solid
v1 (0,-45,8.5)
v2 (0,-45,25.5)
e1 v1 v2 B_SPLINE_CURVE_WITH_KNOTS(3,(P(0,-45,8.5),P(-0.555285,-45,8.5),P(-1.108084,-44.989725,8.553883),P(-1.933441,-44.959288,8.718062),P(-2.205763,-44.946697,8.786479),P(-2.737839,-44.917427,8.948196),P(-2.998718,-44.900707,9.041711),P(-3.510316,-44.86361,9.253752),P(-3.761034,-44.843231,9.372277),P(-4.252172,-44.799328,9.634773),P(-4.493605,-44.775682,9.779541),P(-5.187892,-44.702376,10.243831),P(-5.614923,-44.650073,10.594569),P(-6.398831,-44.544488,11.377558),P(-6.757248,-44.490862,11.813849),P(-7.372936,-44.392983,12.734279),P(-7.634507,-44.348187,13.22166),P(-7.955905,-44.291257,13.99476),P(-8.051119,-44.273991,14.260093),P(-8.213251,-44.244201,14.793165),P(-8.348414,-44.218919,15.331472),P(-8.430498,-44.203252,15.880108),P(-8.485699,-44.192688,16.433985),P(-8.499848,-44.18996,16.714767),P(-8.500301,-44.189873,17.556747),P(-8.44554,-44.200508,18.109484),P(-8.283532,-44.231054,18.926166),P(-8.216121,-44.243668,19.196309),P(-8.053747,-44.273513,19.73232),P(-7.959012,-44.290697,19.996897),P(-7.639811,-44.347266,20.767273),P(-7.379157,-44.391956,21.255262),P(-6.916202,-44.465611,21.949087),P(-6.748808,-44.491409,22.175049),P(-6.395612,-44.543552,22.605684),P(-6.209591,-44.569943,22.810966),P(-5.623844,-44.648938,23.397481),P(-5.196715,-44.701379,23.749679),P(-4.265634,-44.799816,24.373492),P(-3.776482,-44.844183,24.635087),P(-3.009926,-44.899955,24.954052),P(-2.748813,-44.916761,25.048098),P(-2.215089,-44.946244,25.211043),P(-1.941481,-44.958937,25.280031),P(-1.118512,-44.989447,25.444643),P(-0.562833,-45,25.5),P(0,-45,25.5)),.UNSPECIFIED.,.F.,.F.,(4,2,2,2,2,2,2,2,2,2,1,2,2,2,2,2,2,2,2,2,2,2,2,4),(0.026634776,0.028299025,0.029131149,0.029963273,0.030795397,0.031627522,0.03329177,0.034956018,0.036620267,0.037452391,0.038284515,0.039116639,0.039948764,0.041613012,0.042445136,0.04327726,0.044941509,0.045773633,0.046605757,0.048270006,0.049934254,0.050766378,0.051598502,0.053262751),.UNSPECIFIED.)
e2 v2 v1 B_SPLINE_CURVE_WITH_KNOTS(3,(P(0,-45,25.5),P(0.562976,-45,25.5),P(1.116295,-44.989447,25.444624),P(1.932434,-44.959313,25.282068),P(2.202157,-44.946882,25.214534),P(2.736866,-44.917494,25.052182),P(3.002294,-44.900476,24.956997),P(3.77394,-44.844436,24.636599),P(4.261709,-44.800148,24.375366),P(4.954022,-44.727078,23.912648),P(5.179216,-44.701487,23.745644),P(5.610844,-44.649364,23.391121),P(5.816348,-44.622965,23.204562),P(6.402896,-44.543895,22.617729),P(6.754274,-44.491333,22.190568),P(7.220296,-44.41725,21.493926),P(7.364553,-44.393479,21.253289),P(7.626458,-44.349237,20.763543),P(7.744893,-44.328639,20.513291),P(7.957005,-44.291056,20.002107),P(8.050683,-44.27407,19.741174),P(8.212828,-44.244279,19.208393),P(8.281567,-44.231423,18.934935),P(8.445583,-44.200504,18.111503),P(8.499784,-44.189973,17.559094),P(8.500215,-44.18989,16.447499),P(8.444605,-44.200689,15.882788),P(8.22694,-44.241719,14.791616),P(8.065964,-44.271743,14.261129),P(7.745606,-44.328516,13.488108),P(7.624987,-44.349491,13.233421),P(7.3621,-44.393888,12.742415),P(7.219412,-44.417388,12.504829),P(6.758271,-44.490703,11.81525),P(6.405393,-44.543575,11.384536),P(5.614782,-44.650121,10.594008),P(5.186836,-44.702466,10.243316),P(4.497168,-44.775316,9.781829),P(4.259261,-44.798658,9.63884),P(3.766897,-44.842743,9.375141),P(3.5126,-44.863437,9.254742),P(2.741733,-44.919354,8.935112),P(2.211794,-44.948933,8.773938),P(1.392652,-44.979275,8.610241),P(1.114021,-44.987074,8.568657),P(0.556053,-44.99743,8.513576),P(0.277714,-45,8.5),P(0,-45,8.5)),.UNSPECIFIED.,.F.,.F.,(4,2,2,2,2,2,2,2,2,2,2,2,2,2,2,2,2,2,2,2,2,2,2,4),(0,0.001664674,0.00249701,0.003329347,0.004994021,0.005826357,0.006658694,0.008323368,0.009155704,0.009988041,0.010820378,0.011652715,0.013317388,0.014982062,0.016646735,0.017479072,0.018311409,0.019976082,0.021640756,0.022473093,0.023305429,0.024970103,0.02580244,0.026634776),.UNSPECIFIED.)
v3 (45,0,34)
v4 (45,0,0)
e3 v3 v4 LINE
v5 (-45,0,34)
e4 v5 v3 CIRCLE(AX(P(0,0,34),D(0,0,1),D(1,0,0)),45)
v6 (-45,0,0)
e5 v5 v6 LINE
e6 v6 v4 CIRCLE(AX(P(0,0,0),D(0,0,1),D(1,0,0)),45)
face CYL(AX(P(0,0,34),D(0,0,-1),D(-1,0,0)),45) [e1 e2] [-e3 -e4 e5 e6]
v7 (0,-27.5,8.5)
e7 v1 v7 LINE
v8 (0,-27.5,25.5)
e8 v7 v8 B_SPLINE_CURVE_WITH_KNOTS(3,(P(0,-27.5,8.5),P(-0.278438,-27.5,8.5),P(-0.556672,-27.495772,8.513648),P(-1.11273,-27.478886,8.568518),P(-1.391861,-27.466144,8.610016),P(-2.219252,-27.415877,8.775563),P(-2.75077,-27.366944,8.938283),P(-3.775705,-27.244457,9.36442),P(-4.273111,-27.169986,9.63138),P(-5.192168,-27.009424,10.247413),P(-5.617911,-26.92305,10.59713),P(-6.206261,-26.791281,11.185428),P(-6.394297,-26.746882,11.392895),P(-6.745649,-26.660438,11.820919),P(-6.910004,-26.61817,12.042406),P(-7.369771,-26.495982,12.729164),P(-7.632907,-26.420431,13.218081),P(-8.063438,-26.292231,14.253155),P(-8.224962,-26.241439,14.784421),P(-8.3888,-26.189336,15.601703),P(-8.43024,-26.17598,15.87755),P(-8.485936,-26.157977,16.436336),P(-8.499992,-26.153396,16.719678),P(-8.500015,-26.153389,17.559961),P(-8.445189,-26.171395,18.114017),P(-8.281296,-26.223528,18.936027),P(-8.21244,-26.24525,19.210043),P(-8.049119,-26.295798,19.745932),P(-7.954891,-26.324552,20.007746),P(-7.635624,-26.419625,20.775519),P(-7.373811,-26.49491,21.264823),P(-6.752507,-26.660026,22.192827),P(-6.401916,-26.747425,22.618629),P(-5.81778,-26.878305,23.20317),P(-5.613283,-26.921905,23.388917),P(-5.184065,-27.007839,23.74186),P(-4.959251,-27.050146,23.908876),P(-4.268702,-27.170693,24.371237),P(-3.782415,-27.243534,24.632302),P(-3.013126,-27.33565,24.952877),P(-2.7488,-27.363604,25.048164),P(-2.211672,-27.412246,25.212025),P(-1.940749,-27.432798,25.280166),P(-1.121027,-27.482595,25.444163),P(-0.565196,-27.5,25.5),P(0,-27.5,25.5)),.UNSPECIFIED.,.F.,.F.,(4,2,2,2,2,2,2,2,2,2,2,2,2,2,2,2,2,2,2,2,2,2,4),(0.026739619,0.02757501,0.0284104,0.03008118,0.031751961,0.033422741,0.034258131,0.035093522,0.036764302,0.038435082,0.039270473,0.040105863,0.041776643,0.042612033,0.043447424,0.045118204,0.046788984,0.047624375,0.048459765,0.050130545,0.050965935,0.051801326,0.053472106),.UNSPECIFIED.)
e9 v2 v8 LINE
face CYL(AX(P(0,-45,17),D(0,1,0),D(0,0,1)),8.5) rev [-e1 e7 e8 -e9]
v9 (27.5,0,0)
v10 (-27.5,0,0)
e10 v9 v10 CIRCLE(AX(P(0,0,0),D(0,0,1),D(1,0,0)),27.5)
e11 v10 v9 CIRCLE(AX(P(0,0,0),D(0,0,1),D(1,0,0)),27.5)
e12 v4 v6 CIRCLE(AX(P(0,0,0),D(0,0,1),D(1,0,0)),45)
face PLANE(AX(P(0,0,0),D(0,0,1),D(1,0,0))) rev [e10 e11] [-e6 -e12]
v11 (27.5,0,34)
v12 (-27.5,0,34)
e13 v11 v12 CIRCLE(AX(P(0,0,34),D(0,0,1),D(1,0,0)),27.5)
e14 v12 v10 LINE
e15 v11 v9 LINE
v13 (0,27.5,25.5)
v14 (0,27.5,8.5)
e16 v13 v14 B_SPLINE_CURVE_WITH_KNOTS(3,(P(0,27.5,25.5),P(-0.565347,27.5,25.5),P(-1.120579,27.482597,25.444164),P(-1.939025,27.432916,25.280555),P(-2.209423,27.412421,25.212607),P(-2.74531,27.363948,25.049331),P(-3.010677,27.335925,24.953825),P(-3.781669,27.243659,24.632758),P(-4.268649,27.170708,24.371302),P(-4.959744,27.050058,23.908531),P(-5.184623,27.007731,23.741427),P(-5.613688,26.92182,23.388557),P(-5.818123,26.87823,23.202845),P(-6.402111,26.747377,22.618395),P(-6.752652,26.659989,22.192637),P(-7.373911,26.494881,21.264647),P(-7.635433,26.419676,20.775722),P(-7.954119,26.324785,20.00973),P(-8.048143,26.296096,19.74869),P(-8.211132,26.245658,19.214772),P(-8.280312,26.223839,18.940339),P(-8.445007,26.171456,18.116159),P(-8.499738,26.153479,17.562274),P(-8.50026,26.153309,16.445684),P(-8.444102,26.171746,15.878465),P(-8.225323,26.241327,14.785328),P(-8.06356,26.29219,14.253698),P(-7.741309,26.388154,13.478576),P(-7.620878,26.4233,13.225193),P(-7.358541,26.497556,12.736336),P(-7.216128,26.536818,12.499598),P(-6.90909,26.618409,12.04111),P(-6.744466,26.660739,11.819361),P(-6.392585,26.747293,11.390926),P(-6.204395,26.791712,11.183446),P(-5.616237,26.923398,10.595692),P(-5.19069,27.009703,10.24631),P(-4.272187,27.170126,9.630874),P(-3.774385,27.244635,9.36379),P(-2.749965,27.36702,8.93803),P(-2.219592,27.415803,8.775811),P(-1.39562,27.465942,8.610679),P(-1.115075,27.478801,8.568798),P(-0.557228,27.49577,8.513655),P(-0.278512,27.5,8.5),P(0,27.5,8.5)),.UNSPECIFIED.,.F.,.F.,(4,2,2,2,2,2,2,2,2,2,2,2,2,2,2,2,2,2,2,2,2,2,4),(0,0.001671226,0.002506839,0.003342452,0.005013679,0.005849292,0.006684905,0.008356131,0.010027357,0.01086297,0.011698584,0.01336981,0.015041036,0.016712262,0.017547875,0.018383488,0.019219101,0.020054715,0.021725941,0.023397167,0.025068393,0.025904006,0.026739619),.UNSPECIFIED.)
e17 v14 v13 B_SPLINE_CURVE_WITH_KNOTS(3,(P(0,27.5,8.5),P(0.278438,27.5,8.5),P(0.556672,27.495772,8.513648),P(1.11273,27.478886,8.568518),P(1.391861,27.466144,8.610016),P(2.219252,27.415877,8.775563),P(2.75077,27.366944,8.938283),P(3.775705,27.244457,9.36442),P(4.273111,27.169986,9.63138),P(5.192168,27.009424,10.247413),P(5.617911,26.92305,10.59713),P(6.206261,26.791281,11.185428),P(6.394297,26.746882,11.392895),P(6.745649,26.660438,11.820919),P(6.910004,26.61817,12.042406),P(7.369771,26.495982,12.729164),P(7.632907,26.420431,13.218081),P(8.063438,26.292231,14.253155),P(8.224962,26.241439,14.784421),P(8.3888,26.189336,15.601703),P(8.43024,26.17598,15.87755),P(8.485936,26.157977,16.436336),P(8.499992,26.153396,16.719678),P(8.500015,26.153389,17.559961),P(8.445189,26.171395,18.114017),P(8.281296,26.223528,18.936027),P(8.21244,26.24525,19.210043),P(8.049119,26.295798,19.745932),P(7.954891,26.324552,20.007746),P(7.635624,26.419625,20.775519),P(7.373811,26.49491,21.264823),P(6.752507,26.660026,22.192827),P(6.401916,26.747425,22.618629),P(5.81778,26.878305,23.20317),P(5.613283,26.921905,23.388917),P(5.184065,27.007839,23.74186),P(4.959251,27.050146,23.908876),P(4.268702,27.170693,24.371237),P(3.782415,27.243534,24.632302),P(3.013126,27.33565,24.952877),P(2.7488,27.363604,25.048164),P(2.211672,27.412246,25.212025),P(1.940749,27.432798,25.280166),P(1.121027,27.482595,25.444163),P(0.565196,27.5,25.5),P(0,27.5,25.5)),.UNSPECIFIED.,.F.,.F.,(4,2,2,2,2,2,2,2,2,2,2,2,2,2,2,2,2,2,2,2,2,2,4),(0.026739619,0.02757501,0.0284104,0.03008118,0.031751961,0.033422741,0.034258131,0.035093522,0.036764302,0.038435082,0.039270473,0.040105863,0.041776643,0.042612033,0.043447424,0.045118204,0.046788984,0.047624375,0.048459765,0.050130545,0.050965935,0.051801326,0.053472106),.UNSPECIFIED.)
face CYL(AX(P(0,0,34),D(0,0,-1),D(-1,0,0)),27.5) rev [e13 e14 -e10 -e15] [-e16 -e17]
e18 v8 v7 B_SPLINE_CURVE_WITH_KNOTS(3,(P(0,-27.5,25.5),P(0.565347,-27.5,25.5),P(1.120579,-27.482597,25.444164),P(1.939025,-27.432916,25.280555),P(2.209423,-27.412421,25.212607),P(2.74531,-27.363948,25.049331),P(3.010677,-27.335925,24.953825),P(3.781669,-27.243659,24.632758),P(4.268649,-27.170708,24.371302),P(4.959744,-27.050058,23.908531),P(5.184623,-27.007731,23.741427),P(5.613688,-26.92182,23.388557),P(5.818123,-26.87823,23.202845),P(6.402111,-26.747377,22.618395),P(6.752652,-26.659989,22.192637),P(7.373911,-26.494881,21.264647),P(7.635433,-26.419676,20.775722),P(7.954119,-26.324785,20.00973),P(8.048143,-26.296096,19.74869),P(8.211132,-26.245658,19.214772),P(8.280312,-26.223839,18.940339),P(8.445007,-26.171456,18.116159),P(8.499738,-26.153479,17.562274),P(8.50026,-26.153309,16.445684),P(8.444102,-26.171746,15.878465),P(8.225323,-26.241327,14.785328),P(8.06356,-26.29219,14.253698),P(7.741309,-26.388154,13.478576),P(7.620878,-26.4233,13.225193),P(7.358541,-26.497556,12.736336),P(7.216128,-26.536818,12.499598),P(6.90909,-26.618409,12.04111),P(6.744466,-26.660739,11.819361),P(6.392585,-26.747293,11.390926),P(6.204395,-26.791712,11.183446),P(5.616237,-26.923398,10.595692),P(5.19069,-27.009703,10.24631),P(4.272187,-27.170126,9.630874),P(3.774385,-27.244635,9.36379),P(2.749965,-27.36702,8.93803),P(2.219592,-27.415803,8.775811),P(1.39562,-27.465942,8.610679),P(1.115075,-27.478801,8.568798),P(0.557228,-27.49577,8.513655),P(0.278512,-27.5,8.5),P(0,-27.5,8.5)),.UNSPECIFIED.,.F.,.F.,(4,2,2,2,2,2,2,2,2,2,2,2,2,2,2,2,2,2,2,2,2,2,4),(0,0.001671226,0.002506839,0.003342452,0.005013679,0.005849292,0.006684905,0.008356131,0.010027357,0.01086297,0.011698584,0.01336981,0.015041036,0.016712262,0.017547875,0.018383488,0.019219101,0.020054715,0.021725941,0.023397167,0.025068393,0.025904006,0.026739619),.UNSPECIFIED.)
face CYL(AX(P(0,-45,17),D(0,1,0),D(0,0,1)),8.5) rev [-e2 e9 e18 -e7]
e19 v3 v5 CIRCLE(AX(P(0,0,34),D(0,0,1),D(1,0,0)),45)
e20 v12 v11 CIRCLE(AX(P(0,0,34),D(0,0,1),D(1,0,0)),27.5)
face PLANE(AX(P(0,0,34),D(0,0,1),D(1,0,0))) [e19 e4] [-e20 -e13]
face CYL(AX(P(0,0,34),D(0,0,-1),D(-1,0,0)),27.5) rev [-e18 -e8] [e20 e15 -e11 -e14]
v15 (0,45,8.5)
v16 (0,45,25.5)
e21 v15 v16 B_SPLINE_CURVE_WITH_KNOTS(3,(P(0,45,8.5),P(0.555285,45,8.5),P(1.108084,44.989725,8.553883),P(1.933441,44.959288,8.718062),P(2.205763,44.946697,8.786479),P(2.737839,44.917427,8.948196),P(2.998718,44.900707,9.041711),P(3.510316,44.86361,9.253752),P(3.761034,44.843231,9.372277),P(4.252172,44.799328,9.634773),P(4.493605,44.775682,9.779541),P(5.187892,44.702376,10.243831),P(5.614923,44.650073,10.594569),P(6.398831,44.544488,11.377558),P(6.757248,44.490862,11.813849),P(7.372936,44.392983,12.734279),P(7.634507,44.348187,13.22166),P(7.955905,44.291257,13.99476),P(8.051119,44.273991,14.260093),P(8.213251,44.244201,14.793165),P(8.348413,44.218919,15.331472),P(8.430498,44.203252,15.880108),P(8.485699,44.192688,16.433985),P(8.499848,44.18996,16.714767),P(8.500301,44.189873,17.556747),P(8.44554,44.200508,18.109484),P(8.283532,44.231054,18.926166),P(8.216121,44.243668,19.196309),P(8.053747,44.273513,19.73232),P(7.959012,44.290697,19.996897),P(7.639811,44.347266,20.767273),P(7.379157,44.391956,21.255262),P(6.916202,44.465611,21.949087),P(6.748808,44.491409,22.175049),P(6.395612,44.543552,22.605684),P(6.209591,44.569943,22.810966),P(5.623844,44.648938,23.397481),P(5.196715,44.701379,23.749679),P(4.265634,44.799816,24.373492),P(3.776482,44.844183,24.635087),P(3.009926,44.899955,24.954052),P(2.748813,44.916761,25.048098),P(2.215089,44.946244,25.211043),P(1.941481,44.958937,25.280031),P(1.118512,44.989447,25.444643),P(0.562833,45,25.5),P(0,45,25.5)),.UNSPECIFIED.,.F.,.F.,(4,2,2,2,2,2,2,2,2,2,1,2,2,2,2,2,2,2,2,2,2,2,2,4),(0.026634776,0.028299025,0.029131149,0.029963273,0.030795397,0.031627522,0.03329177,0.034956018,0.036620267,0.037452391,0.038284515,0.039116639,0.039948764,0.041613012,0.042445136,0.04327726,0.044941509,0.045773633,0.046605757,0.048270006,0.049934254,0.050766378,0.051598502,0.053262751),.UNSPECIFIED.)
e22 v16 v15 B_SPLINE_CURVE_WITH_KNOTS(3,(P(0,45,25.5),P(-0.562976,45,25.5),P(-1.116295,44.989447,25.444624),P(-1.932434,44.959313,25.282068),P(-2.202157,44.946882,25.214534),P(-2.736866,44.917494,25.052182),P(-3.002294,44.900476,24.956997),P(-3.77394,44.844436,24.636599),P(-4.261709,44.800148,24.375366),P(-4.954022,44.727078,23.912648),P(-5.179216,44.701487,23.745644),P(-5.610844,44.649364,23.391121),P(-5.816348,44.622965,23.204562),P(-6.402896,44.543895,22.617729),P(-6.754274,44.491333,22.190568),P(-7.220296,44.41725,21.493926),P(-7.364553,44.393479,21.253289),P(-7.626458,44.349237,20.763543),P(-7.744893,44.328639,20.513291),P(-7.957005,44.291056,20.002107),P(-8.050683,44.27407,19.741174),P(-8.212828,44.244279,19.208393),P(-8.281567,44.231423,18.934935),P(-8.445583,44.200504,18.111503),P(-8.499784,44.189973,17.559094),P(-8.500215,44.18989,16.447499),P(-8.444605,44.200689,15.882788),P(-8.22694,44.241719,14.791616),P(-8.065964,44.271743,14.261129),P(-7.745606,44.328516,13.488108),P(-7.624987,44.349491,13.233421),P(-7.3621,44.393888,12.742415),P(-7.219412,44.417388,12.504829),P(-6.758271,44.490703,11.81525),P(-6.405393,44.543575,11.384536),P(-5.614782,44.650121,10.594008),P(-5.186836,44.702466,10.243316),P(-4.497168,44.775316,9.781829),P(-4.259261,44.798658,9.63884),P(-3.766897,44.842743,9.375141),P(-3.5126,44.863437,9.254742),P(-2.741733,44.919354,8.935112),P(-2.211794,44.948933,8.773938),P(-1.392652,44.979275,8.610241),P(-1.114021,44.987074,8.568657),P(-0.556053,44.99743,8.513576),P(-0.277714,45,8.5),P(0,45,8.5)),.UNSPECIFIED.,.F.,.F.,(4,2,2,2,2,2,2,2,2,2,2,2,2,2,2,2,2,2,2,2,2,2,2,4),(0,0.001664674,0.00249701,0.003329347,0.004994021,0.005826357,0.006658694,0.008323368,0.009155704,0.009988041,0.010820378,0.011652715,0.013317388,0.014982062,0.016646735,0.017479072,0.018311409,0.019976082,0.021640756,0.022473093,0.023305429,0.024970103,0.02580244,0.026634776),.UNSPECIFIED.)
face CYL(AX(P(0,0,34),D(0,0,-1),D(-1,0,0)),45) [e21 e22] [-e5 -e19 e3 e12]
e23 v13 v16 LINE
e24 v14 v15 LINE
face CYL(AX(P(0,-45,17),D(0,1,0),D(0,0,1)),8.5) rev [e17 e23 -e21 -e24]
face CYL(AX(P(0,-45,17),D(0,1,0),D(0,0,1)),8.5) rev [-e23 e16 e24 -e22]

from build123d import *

# Parameters (mm, degrees)
SKETCH2_R               = 45
SKETCH2_R_2             = 27.5
BOSS_EXTRUDE1_DEPTH     = 34
CUT_EXTRUDE1_DEPTH      = 73.15261603
CUT_EXTRUDE1_DEPTH_BACK = 73.15261603
SKETCH3_R               = 8.5


with BuildPart() as part:
    # Sketch2 → Boss-Extrude1 (new body)
    with BuildSketch(Plane.XY):
        Circle(SKETCH2_R)
        Circle(SKETCH2_R_2, mode=Mode.SUBTRACT)
    extrude(amount=BOSS_EXTRUDE1_DEPTH)

    # Sketch3 → Cut-Extrude1 (cut, two sides: drawn at the far end of the back side and taken through both)
    with BuildSketch(Plane(origin=(0, 0, 0), x_dir=(1, 0, 0), z_dir=(0, 1, 0)).offset(-CUT_EXTRUDE1_DEPTH_BACK)):
        with Locations(Location((0, -17, 0), (0, 0, 270))):
            Circle(SKETCH3_R)
    extrude(amount=CUT_EXTRUDE1_DEPTH + CUT_EXTRUDE1_DEPTH_BACK, mode=Mode.SUBTRACT)


solid = part.part
